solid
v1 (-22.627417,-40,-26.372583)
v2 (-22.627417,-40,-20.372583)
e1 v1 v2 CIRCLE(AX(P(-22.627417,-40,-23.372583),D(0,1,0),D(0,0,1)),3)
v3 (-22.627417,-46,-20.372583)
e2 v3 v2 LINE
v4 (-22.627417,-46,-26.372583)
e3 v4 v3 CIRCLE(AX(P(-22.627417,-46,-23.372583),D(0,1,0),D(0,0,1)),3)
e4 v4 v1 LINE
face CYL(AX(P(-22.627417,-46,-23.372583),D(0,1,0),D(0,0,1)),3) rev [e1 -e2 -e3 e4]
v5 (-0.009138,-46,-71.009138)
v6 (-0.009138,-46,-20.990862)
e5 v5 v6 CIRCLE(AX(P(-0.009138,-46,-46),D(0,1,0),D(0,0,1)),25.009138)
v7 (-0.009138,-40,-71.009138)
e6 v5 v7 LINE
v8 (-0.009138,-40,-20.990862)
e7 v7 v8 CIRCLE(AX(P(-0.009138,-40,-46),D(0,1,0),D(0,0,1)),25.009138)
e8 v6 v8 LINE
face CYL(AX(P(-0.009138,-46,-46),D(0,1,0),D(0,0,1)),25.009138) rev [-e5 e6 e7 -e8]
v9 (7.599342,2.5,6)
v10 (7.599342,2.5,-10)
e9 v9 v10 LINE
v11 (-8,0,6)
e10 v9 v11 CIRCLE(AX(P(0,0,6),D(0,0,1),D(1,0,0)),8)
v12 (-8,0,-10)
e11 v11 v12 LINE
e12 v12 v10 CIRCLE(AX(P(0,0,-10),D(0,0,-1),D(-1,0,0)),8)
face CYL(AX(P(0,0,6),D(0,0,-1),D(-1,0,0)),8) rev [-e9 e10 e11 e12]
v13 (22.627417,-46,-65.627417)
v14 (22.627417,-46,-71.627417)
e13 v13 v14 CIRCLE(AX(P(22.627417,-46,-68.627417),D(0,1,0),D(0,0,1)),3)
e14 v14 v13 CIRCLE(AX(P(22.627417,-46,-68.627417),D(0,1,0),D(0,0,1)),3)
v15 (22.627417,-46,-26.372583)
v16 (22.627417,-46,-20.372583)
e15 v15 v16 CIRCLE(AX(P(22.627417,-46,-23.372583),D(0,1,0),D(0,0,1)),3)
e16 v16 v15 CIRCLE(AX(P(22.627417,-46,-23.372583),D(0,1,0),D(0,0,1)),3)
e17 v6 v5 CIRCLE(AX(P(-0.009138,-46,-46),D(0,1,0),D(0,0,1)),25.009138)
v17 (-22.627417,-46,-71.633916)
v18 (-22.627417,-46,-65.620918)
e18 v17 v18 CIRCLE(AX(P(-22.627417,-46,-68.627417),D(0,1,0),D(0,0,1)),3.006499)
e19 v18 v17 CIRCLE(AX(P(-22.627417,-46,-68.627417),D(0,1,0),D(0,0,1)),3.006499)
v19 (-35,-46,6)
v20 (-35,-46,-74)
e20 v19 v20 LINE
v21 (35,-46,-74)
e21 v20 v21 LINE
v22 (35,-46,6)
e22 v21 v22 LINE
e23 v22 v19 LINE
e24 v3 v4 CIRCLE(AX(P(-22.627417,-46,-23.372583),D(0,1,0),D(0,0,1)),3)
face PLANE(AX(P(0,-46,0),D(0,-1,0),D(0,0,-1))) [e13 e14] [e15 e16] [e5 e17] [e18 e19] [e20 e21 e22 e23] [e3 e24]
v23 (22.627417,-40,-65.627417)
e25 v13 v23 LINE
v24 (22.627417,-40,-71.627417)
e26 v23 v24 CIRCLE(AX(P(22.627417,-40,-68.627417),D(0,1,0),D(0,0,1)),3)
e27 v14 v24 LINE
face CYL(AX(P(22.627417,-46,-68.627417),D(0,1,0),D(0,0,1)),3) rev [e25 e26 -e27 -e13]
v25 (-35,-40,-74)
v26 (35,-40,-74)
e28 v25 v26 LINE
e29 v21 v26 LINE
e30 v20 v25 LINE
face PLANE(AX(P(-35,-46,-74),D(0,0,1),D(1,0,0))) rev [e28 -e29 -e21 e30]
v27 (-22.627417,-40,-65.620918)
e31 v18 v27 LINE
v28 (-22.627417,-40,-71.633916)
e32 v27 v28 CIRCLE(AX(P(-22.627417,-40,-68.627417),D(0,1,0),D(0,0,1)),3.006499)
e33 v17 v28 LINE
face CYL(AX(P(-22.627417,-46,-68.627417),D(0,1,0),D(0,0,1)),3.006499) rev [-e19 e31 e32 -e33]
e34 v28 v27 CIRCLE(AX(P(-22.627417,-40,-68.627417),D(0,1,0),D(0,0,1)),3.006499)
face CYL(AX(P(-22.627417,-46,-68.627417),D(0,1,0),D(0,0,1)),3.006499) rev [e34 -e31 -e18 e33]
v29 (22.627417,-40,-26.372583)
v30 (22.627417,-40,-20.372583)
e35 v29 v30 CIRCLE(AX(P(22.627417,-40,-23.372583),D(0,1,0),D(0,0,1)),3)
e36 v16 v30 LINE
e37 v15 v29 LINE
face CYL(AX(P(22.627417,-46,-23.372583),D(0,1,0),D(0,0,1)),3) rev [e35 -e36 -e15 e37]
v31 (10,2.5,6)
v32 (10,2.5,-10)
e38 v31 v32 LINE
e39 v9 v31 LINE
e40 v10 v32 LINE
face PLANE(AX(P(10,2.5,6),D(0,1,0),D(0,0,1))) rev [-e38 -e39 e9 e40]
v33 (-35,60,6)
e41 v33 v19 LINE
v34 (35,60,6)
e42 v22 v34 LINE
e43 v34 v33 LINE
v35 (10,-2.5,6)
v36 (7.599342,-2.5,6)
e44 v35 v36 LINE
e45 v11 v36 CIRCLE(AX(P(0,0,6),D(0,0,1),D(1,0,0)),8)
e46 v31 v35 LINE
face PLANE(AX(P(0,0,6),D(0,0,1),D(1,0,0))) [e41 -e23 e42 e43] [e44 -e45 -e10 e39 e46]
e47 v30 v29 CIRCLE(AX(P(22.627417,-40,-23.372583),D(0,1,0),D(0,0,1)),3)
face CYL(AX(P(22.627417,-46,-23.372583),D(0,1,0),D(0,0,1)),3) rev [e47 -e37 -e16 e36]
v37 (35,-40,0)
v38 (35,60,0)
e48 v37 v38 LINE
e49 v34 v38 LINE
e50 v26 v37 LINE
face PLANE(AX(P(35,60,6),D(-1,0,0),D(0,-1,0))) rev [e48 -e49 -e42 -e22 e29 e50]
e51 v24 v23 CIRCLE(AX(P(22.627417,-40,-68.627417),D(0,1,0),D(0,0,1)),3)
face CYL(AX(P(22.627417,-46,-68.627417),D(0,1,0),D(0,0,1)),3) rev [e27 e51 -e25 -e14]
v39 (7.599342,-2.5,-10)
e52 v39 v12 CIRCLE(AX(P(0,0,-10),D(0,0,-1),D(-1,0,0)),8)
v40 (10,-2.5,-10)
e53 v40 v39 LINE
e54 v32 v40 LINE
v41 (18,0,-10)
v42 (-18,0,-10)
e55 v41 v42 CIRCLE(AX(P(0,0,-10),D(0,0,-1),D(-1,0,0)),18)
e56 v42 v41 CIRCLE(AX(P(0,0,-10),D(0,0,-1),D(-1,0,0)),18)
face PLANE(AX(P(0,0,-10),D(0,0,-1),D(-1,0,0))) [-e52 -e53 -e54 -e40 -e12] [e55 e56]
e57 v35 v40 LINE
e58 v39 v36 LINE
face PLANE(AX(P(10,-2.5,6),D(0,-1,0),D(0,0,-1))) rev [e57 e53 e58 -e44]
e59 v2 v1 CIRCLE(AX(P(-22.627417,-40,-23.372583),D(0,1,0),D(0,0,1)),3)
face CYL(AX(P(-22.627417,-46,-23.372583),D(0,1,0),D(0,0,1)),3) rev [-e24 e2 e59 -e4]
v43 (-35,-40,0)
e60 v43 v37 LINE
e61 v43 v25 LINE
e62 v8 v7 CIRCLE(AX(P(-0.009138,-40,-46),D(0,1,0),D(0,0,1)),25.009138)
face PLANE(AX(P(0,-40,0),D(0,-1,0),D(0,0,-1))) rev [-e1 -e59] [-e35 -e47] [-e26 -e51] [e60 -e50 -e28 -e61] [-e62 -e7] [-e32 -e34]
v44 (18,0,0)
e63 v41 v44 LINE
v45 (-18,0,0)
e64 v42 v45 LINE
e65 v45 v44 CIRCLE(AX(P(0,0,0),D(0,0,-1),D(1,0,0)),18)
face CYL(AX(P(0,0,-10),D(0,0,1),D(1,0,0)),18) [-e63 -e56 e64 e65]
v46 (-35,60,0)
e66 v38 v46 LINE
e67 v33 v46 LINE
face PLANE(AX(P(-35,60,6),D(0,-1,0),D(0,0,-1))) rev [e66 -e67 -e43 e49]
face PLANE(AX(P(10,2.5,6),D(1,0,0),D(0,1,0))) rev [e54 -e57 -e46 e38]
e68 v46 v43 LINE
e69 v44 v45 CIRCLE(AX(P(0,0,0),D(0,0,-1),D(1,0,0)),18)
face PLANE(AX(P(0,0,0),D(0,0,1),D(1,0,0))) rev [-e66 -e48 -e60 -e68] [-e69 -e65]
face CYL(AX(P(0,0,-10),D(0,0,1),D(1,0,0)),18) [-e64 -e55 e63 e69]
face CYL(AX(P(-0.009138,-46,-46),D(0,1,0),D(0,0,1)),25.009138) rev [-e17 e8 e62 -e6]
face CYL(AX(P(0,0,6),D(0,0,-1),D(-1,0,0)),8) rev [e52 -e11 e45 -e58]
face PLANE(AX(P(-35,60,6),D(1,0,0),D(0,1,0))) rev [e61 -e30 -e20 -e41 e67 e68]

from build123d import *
from build123d.topology import SkipClean

# Parameters (mm, degrees)
SKETCH1_W           = 70
SKETCH1_H           = 100
SKETCH1_R           = 8
BOSS_EXTRUDE1_DEPTH = 6
BOSS_EXTRUDE2_START = 10
SKETCH2_R           = 18
SKETCH2_R_2         = 8
BOSS_EXTRUDE2_DEPTH = 10
SKETCH3_W           = 70
SKETCH3_H           = 80
BOSS_EXTRUDE3_DEPTH = 6
SKETCH4_W           = 4.928950204
SKETCH4_H           = 5
CUT_EXTRUDE1_DEPTH  = 95.451045521
SKETCH5_R           = 3.006498603
SKETCH5_R_2         = 3
SKETCH5_R_3         = 25.009138209
CUT_EXTRUDE2_DEPTH  = 6


with BuildPart() as part:
    # Sketch1 → Boss-Extrude1 (new body)
    with BuildSketch(Plane.XY):
        with Locations((0, 10)):
            Rectangle(SKETCH1_W, SKETCH1_H)
        Circle(SKETCH1_R, mode=Mode.SUBTRACT)
    extrude(amount=BOSS_EXTRUDE1_DEPTH)

    # Sketch2 → Boss-Extrude2 (add)
    with SkipClean():  # the faces are left unmerged after this step: merging them gives an invalid solid
        with BuildSketch(Plane(origin=(0, 0, 0), x_dir=(-1, 0, 0), z_dir=(0, 0, -1)).offset(BOSS_EXTRUDE2_START)):
            with Locations(Location((0, 0, 0), (0, 0, 180))):
                Circle(SKETCH2_R)
            Circle(SKETCH2_R_2, mode=Mode.SUBTRACT)
        extrude(amount=-BOSS_EXTRUDE2_DEPTH)

    # Sketch3 → Boss-Extrude3 (add)
    with SkipClean():  # the faces are left unmerged after this step: merging them gives an invalid solid
        with BuildSketch(Plane.XZ.offset(40)):
            with Locations((0, -34)):
                Rectangle(SKETCH3_W, SKETCH3_H)
        extrude(amount=BOSS_EXTRUDE3_DEPTH)

    # Sketch4 → Cut-Extrude1 (cut, through all)
    with BuildSketch(Plane(origin=(0, 0, -10), x_dir=(-1, 0, 0), z_dir=(0, 0, -1))):
        with Locations((-7.535524898, 0)):
            Rectangle(SKETCH4_W, SKETCH4_H)
    extrude(amount=-CUT_EXTRUDE1_DEPTH, mode=Mode.SUBTRACT)

    # Sketch5 → Cut-Extrude2 (cut)
    with BuildSketch(Plane(origin=(0, -40, 0), x_dir=(1, 0, 0), z_dir=(0, 1, 0))):
        with Locations(Location((-22.627416998, 68.627416998, 0), (0, 0, 270))):
            Circle(SKETCH5_R)
        with Locations(Location((22.627416998, 68.627416998, 0), (0, 0, 270))):
            Circle(SKETCH5_R_2)
        with Locations(Location((22.627416998, 23.372583002, 0), (0, 0, 270))):
            Circle(SKETCH5_R_2)
        with Locations(Location((-22.627416998, 23.372583002, 0), (0, 0, 270))):
            Circle(SKETCH5_R_2)
        with Locations(Location((-0.009138209, 46.00000012, 0), (0, 0, 270))):
            Circle(SKETCH5_R_3)
    extrude(amount=-CUT_EXTRUDE2_DEPTH, mode=Mode.SUBTRACT)


solid = part.part
